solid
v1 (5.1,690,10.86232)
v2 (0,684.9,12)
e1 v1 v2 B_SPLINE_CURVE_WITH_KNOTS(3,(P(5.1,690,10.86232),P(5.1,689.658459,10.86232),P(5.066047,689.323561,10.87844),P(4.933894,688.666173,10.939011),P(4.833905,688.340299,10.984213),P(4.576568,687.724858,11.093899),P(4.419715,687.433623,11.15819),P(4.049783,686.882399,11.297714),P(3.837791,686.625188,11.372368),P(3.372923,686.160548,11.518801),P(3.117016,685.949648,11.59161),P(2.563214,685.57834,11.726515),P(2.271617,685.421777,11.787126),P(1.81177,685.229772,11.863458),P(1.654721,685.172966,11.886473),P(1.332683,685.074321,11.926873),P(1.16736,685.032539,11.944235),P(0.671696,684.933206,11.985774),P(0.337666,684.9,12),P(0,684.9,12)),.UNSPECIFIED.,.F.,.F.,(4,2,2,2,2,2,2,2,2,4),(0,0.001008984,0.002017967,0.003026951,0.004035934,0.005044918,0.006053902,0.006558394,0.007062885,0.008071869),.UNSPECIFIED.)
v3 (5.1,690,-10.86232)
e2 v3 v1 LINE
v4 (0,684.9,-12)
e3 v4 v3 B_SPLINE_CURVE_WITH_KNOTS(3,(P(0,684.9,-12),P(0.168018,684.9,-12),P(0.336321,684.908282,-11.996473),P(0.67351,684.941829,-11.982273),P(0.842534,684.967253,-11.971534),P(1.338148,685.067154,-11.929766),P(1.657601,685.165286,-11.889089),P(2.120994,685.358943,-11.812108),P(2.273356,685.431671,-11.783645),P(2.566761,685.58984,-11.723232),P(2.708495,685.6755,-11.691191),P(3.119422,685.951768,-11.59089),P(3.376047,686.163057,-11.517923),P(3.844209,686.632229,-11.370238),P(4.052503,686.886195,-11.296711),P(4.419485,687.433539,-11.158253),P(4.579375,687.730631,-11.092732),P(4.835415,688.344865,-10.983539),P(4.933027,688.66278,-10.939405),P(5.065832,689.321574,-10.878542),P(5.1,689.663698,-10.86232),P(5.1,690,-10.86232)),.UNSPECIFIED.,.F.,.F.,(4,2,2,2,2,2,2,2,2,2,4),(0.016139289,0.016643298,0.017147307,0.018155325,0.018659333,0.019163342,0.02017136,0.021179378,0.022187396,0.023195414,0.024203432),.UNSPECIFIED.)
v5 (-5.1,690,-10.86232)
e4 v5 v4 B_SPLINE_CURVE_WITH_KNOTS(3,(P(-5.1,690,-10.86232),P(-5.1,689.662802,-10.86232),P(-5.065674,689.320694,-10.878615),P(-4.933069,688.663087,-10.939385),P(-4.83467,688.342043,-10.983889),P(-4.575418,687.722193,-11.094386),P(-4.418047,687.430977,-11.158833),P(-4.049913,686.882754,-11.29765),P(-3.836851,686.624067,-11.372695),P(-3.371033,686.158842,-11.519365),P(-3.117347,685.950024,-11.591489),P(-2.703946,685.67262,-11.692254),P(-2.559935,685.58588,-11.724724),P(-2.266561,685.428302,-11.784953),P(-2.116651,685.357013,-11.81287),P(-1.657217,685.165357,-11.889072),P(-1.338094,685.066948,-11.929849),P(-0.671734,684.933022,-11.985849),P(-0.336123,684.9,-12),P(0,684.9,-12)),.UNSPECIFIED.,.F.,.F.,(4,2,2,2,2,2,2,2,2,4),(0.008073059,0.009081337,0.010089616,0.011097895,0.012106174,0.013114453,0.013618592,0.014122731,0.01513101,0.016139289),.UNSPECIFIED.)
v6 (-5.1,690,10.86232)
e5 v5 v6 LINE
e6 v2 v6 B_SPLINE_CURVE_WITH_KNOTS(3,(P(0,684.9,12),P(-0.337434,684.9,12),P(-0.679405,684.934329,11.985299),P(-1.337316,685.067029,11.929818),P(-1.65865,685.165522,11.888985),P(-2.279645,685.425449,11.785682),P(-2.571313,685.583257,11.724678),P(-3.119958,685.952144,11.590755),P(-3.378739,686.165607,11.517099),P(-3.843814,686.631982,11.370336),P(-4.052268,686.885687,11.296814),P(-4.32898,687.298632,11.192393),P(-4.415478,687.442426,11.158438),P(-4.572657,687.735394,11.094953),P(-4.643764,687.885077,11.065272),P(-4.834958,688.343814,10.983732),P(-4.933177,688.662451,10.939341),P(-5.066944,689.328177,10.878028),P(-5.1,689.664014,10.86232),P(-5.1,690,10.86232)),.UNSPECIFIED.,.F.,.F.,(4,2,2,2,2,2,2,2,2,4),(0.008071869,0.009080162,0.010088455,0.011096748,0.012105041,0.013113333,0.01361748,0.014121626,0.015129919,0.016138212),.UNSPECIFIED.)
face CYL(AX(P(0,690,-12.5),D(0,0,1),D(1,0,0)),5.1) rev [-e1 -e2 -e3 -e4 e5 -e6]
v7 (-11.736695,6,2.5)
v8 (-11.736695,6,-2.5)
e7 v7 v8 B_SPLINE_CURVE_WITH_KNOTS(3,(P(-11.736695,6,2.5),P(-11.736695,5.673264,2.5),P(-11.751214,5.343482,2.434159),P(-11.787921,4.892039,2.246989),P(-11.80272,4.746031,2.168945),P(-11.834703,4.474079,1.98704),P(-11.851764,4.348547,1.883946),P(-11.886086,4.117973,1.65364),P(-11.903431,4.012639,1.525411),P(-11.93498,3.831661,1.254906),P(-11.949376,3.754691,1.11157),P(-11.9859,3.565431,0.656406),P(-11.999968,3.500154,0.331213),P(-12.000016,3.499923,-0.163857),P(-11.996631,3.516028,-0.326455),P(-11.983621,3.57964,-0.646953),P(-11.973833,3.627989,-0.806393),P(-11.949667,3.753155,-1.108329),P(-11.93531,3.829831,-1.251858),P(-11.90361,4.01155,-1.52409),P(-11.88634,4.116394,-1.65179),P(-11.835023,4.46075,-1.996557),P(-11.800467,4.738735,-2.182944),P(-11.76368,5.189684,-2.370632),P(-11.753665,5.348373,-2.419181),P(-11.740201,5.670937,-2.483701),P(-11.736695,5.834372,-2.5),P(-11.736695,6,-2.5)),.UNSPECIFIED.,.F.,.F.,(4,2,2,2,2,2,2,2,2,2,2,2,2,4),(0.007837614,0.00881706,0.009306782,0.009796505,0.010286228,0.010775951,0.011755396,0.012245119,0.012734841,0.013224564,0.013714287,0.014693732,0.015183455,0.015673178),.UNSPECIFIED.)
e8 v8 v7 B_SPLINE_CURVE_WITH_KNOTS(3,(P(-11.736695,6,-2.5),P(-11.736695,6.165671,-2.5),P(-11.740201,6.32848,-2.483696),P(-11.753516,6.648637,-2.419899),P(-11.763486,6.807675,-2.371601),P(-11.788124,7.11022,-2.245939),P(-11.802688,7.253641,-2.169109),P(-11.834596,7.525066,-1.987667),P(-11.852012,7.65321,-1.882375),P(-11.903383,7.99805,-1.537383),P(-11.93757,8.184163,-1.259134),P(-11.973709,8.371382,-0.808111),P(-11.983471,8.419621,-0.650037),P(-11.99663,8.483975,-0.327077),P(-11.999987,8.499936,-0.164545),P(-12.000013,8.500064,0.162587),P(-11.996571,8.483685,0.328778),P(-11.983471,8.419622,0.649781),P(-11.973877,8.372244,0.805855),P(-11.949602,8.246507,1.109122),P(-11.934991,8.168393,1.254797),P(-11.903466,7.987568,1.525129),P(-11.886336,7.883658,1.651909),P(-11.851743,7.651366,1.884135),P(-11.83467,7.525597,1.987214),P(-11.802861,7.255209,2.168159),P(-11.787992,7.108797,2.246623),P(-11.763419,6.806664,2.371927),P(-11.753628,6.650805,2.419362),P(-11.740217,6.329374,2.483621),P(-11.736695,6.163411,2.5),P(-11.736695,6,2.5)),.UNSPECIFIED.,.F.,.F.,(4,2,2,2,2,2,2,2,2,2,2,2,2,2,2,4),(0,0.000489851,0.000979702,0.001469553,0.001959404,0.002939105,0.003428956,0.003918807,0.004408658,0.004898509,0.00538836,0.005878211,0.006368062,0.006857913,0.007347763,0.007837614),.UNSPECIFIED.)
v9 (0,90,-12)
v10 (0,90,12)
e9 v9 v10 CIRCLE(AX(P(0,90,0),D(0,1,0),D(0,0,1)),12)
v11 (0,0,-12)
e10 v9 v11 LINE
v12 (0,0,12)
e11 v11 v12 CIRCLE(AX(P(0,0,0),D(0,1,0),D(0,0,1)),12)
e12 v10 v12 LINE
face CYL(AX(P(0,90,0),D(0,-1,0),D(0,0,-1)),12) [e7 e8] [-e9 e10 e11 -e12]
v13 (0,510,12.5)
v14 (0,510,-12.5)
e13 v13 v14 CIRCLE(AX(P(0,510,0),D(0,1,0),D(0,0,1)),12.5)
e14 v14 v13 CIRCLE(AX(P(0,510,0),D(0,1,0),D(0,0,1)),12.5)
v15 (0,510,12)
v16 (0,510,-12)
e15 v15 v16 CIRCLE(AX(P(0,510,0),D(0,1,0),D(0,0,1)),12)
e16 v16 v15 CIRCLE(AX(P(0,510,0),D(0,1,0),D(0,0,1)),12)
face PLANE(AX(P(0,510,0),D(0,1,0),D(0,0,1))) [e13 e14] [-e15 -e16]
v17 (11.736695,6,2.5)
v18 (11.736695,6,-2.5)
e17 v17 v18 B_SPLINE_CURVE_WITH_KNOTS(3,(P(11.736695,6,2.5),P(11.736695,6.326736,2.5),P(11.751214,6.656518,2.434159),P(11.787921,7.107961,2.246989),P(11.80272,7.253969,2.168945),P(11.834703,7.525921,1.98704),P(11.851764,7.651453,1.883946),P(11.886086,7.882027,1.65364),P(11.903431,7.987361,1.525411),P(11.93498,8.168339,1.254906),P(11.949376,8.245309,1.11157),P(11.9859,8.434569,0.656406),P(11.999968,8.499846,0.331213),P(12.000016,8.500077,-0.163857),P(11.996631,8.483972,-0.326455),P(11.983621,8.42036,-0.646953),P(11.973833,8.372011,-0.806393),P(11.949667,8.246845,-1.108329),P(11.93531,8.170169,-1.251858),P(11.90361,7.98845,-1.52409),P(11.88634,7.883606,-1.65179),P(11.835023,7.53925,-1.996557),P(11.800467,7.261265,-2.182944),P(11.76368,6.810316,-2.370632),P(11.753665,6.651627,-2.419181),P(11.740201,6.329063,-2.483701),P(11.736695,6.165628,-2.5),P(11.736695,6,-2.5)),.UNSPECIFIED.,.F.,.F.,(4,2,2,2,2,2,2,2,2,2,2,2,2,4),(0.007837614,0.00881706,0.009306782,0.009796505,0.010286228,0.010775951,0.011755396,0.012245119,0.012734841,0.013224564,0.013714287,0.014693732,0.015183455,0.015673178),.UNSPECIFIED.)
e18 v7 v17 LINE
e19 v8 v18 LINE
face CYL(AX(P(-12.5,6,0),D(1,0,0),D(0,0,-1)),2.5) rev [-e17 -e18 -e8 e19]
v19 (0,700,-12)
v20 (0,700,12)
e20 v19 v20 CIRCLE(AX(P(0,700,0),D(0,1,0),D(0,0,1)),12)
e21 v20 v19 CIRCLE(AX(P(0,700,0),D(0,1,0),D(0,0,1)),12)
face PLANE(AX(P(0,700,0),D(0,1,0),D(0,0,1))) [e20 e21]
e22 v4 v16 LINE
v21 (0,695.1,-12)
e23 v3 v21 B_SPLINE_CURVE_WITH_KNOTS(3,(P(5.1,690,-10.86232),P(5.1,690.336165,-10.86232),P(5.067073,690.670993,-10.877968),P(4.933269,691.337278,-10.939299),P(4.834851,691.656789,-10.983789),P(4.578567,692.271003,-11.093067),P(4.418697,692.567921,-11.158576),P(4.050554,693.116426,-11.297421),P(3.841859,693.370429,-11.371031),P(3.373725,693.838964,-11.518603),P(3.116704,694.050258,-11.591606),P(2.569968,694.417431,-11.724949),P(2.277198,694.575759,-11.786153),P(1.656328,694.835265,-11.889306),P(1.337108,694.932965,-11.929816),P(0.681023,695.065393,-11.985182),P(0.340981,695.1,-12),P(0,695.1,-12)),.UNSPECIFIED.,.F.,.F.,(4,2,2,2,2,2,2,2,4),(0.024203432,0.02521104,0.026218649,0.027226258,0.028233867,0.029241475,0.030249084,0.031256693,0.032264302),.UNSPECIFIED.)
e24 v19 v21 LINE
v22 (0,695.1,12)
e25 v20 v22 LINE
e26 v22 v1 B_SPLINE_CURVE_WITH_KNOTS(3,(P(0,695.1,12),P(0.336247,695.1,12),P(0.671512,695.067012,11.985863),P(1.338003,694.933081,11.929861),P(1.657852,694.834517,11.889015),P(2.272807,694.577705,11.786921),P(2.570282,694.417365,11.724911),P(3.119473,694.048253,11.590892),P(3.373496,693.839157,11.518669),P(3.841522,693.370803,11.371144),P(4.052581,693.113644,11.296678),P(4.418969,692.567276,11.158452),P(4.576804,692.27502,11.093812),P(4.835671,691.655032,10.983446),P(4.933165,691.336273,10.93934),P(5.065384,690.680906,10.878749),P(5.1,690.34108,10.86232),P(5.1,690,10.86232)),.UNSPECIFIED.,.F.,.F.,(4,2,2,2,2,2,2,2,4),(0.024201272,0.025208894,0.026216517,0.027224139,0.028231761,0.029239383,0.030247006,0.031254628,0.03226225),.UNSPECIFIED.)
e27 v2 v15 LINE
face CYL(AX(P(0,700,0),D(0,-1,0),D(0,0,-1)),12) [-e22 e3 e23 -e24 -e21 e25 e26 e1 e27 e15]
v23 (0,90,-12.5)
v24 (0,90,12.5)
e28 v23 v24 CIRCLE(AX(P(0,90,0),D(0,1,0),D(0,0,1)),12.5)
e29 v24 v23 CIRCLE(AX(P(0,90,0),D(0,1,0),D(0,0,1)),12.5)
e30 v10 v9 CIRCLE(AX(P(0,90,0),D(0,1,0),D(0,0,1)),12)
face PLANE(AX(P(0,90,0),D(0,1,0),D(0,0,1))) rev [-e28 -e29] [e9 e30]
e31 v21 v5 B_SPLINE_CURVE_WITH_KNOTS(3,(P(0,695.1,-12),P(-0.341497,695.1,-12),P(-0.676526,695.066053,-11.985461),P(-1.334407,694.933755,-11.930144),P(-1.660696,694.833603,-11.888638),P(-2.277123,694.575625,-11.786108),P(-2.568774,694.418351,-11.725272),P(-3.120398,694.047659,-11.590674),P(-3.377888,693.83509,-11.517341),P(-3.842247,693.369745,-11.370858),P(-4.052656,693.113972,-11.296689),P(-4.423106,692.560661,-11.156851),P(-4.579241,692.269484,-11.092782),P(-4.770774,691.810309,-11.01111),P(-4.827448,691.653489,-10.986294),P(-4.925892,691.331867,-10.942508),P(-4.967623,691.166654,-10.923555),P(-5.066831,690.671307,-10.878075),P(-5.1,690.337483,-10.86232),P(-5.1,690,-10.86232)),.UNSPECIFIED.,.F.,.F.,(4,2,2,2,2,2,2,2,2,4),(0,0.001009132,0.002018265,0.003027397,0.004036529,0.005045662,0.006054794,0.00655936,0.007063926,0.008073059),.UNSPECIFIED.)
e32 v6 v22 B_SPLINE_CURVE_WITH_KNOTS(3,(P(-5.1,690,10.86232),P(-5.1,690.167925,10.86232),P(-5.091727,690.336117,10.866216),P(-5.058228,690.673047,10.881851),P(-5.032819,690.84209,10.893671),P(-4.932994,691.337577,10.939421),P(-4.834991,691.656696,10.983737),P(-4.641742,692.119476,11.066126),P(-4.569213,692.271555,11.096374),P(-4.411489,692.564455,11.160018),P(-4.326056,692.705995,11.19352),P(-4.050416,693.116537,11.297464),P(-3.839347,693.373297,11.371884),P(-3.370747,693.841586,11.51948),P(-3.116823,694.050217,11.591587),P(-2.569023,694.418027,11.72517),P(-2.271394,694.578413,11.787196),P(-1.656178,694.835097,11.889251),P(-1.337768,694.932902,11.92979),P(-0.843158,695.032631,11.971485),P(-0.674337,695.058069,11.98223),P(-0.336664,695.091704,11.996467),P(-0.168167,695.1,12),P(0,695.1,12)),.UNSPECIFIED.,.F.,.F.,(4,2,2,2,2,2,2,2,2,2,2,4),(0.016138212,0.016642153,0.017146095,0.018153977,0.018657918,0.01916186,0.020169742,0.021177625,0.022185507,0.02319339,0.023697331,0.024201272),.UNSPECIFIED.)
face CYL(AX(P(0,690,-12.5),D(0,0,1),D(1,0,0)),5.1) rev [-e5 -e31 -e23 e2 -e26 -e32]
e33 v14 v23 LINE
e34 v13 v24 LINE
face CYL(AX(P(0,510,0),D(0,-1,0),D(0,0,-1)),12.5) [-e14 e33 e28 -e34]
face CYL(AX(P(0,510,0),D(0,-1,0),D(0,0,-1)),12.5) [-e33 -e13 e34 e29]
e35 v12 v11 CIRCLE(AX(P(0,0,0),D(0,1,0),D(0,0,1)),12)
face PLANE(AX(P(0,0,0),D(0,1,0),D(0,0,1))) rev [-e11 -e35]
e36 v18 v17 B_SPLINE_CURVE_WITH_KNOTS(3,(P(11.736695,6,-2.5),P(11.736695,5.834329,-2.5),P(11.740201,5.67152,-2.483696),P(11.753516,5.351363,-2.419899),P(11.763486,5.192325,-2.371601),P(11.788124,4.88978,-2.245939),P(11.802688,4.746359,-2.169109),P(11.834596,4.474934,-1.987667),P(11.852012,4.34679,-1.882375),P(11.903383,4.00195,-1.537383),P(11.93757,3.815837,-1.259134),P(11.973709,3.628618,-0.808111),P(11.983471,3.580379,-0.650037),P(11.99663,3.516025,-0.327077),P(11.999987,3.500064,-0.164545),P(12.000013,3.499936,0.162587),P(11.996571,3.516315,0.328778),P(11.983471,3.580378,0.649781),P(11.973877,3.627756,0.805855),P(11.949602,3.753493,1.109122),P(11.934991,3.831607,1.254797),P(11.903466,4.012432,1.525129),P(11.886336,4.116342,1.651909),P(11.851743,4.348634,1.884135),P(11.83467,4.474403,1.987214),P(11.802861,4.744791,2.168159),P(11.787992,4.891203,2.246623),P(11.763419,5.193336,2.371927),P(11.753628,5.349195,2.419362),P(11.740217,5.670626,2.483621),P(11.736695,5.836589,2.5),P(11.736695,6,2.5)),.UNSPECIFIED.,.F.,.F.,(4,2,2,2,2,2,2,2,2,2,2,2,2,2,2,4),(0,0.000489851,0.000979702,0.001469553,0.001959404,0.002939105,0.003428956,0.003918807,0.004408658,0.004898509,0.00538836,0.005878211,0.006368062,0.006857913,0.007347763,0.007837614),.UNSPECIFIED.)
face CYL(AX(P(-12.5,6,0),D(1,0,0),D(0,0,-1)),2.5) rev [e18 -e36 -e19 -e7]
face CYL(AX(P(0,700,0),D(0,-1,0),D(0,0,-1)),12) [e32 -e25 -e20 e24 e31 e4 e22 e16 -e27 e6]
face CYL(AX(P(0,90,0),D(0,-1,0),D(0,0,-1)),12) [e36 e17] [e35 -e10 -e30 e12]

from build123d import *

# Parameters (mm, degrees)
SKETCH1_R               = 12
BOSS_EXTRUDE1_DEPTH     = 90
SKETCH2_R               = 12.5
BOSS_EXTRUDE2_DEPTH     = 420
SKETCH3_R               = 12
BOSS_EXTRUDE3_DEPTH     = 190
CUT_EXTRUDE1_DEPTH      = 701.223178708
CUT_EXTRUDE1_DEPTH_BACK = 701.223178708
SKETCH4_R               = 5.1
CUT_EXTRUDE2_DEPTH      = 701.223178808
CUT_EXTRUDE2_DEPTH_BACK = 701.223178808
SKETCH5_R               = 2.5


with BuildPart() as part:
    # Sketch1 → Boss-Extrude1 (new body)
    with BuildSketch(Plane(origin=(0, 0, 0), x_dir=(1, 0, 0), z_dir=(0, 1, 0))):
        with Locations(Location((0, 0, 0), (0, 0, 90))):
            Circle(SKETCH1_R)
    extrude(amount=BOSS_EXTRUDE1_DEPTH)

    # Sketch2 → Boss-Extrude2 (add)
    with BuildSketch(Plane(origin=(0, 90, 0), x_dir=(1, 0, 0), z_dir=(0, 1, 0))):
        with Locations(Location((0, 0, 0), (0, 0, 270))):
            Circle(SKETCH2_R)
    extrude(amount=BOSS_EXTRUDE2_DEPTH)

    # Sketch3 → Boss-Extrude3 (add)
    with BuildSketch(Plane(origin=(0, 510, 0), x_dir=(1, 0, 0), z_dir=(0, 1, 0))):
        with Locations(Location((0, 0, 0), (0, 0, 90))):
            Circle(SKETCH3_R)
    extrude(amount=BOSS_EXTRUDE3_DEPTH)

    # Sketch4 → Cut-Extrude1 (cut, two sides: drawn at the far end of the back side and taken through both)
    with BuildSketch(Plane.XY.offset(-CUT_EXTRUDE1_DEPTH_BACK)):
        with Locations(Location((0, 690, 0), (0, 0, 90))):
            Circle(SKETCH4_R)
    extrude(amount=CUT_EXTRUDE1_DEPTH + CUT_EXTRUDE1_DEPTH_BACK, mode=Mode.SUBTRACT)

    # Sketch5 → Cut-Extrude2 (cut, two sides: drawn at the far end of the back side and taken through both)
    with BuildSketch(Plane(origin=(0, 0, 0), x_dir=(0, 0, -1), z_dir=(1, 0, 0)).offset(-CUT_EXTRUDE2_DEPTH_BACK)):
        with Locations((0, 6)):
            Circle(SKETCH5_R)
    extrude(amount=CUT_EXTRUDE2_DEPTH + CUT_EXTRUDE2_DEPTH_BACK, mode=Mode.SUBTRACT)


solid = part.part
